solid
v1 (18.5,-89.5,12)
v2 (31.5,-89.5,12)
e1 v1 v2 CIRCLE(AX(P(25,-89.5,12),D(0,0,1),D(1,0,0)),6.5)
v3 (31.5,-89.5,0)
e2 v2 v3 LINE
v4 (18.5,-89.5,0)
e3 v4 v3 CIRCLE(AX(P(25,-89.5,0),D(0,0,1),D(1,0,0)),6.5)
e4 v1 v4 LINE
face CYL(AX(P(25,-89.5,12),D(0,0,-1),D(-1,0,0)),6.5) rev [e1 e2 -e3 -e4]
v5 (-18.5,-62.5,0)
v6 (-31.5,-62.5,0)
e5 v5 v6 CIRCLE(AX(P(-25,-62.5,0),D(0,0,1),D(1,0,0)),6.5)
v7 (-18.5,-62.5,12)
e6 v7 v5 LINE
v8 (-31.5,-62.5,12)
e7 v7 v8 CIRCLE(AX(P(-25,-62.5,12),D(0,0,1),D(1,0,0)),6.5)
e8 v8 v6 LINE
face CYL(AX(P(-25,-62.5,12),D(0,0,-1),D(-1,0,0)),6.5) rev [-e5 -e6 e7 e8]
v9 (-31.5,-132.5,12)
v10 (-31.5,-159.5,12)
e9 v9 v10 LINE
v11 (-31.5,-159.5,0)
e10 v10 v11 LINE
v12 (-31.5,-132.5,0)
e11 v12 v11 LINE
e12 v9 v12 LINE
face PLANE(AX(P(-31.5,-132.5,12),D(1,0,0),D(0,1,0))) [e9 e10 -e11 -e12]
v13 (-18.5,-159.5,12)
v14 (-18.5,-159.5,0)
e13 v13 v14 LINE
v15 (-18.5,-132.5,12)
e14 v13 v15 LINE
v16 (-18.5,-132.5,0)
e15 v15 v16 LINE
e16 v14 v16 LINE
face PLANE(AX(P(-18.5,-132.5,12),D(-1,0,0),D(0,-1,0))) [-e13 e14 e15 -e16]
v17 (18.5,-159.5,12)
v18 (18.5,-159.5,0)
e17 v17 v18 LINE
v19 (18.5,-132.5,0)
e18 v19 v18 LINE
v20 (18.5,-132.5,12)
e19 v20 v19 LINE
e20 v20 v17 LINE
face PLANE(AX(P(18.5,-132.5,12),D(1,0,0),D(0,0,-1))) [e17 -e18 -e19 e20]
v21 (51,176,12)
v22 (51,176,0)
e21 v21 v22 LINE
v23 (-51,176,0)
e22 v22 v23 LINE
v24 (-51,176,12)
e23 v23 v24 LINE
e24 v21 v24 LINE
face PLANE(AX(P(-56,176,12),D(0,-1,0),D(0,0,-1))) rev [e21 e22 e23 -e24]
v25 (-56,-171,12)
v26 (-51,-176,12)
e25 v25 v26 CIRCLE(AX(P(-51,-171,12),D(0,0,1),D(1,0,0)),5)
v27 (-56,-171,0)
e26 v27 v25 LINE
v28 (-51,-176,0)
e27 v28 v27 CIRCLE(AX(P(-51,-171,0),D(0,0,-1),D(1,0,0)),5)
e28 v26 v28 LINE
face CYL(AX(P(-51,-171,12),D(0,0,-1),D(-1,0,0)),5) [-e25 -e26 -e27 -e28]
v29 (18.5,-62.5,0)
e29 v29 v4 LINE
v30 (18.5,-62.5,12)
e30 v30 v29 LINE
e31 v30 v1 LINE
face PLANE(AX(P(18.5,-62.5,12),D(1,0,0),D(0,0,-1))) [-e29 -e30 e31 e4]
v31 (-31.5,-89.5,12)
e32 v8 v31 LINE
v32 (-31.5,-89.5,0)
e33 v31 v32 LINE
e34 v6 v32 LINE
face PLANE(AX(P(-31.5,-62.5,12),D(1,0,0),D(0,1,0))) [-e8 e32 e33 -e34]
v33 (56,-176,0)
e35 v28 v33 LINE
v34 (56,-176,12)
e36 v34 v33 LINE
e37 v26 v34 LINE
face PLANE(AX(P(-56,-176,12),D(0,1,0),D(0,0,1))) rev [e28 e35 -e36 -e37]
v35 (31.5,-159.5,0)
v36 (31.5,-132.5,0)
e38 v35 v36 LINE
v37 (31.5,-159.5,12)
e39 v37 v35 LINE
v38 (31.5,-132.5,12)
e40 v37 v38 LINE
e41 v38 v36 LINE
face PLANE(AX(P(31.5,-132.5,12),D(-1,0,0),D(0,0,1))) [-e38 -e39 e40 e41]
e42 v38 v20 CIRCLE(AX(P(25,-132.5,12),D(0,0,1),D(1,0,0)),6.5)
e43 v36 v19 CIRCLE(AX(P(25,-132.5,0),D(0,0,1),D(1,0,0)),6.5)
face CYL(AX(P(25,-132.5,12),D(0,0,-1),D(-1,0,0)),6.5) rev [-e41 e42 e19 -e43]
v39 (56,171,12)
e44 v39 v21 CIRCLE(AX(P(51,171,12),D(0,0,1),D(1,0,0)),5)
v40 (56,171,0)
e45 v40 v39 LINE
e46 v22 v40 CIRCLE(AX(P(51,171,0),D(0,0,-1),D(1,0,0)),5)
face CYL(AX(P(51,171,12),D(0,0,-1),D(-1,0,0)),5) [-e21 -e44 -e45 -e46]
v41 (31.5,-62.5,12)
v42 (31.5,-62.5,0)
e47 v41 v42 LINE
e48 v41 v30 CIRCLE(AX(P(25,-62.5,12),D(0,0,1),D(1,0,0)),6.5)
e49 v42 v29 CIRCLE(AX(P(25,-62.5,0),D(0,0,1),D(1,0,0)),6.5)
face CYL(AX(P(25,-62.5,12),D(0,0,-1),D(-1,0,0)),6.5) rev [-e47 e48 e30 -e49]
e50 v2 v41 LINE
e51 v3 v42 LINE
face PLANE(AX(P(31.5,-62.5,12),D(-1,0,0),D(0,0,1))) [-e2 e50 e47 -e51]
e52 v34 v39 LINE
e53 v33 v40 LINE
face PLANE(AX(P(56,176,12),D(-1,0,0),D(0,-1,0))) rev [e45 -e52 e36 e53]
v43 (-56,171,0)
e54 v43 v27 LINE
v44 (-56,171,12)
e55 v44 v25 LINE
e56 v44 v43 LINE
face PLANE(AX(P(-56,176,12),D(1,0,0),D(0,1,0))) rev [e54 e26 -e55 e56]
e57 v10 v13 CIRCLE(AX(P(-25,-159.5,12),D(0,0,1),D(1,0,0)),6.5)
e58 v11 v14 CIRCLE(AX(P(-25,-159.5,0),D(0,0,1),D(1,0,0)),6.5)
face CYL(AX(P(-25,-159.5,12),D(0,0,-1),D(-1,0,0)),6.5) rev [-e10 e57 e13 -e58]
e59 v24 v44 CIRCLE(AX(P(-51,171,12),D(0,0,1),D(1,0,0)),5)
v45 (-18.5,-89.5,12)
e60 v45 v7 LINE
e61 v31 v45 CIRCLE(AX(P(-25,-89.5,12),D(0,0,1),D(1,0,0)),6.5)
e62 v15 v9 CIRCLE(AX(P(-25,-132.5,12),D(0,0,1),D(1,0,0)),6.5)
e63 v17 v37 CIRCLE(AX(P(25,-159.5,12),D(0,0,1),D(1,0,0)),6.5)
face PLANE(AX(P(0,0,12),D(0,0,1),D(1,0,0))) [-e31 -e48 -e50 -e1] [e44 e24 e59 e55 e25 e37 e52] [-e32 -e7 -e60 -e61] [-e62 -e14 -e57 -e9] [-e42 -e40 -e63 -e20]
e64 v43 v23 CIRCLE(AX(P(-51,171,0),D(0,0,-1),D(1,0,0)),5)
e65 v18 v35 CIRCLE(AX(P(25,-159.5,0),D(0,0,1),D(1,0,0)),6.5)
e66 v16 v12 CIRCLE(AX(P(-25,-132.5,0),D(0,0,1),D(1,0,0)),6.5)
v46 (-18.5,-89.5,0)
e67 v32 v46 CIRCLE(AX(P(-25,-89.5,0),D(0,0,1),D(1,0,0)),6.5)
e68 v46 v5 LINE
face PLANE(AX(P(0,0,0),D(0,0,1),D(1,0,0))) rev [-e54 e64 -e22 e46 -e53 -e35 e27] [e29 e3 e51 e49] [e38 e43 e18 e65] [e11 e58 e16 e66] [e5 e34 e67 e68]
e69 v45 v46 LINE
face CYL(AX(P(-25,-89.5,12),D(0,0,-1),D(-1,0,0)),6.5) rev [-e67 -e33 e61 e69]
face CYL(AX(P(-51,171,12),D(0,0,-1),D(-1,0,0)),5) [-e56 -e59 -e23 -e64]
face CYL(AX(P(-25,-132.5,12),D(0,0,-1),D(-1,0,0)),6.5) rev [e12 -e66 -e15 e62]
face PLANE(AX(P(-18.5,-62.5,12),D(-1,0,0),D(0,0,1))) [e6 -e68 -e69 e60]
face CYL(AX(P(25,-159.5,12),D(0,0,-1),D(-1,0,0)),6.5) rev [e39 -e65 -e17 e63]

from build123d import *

# Parameters (mm, degrees)
SKETCH1_W           = 112
SKETCH1_H           = 352
BOSS_EXTRUDE1_DEPTH = 12
FILLET1_R           = 5


with BuildPart() as part:
    # Sketch1 → Boss-Extrude1 (new body)
    with BuildSketch(Plane.XY):
        Rectangle(SKETCH1_W, SKETCH1_H)
        with BuildLine():
            Line((-18.5, -62.5), (-18.5, -89.5))
            ThreePointArc((-18.5, -89.5), (-25, -96), (-31.5, -89.5))
            Line((-31.5, -89.5), (-31.5, -62.5))
            ThreePointArc((-31.5, -62.5), (-25, -56), (-18.5, -62.5))
        make_face(mode=Mode.SUBTRACT)
        with BuildLine():
            Line((31.5, -62.5), (31.5, -89.5))
            ThreePointArc((31.5, -89.5), (25, -96), (18.5, -89.5))
            Line((18.5, -89.5), (18.5, -62.5))
            ThreePointArc((18.5, -62.5), (25, -56), (31.5, -62.5))
        make_face(mode=Mode.SUBTRACT)
        with BuildLine():
            Line((-31.5, -132.5), (-31.5, -159.5))
            ThreePointArc((-31.5, -159.5), (-25, -166), (-18.5, -159.5))
            Line((-18.5, -159.5), (-18.5, -132.5))
            ThreePointArc((-18.5, -132.5), (-25, -126), (-31.5, -132.5))
        make_face(mode=Mode.SUBTRACT)
        with BuildLine():
            Line((18.5, -132.5), (18.5, -159.5))
            ThreePointArc((18.5, -159.5), (25, -166), (31.5, -159.5))
            Line((31.5, -159.5), (31.5, -132.5))
            ThreePointArc((31.5, -132.5), (25, -126), (18.5, -132.5))
        make_face(mode=Mode.SUBTRACT)
    extrude(amount=BOSS_EXTRUDE1_DEPTH)

    # Fillet1
    fillet1_edges = [part.edges().sort_by_distance(p)[0] for p in [
        (-56, -176, 6),
        (-56, 176, 6),
        (56, 176, 6),
    ]]
    fillet(fillet1_edges, radius=FILLET1_R)


solid = part.part
